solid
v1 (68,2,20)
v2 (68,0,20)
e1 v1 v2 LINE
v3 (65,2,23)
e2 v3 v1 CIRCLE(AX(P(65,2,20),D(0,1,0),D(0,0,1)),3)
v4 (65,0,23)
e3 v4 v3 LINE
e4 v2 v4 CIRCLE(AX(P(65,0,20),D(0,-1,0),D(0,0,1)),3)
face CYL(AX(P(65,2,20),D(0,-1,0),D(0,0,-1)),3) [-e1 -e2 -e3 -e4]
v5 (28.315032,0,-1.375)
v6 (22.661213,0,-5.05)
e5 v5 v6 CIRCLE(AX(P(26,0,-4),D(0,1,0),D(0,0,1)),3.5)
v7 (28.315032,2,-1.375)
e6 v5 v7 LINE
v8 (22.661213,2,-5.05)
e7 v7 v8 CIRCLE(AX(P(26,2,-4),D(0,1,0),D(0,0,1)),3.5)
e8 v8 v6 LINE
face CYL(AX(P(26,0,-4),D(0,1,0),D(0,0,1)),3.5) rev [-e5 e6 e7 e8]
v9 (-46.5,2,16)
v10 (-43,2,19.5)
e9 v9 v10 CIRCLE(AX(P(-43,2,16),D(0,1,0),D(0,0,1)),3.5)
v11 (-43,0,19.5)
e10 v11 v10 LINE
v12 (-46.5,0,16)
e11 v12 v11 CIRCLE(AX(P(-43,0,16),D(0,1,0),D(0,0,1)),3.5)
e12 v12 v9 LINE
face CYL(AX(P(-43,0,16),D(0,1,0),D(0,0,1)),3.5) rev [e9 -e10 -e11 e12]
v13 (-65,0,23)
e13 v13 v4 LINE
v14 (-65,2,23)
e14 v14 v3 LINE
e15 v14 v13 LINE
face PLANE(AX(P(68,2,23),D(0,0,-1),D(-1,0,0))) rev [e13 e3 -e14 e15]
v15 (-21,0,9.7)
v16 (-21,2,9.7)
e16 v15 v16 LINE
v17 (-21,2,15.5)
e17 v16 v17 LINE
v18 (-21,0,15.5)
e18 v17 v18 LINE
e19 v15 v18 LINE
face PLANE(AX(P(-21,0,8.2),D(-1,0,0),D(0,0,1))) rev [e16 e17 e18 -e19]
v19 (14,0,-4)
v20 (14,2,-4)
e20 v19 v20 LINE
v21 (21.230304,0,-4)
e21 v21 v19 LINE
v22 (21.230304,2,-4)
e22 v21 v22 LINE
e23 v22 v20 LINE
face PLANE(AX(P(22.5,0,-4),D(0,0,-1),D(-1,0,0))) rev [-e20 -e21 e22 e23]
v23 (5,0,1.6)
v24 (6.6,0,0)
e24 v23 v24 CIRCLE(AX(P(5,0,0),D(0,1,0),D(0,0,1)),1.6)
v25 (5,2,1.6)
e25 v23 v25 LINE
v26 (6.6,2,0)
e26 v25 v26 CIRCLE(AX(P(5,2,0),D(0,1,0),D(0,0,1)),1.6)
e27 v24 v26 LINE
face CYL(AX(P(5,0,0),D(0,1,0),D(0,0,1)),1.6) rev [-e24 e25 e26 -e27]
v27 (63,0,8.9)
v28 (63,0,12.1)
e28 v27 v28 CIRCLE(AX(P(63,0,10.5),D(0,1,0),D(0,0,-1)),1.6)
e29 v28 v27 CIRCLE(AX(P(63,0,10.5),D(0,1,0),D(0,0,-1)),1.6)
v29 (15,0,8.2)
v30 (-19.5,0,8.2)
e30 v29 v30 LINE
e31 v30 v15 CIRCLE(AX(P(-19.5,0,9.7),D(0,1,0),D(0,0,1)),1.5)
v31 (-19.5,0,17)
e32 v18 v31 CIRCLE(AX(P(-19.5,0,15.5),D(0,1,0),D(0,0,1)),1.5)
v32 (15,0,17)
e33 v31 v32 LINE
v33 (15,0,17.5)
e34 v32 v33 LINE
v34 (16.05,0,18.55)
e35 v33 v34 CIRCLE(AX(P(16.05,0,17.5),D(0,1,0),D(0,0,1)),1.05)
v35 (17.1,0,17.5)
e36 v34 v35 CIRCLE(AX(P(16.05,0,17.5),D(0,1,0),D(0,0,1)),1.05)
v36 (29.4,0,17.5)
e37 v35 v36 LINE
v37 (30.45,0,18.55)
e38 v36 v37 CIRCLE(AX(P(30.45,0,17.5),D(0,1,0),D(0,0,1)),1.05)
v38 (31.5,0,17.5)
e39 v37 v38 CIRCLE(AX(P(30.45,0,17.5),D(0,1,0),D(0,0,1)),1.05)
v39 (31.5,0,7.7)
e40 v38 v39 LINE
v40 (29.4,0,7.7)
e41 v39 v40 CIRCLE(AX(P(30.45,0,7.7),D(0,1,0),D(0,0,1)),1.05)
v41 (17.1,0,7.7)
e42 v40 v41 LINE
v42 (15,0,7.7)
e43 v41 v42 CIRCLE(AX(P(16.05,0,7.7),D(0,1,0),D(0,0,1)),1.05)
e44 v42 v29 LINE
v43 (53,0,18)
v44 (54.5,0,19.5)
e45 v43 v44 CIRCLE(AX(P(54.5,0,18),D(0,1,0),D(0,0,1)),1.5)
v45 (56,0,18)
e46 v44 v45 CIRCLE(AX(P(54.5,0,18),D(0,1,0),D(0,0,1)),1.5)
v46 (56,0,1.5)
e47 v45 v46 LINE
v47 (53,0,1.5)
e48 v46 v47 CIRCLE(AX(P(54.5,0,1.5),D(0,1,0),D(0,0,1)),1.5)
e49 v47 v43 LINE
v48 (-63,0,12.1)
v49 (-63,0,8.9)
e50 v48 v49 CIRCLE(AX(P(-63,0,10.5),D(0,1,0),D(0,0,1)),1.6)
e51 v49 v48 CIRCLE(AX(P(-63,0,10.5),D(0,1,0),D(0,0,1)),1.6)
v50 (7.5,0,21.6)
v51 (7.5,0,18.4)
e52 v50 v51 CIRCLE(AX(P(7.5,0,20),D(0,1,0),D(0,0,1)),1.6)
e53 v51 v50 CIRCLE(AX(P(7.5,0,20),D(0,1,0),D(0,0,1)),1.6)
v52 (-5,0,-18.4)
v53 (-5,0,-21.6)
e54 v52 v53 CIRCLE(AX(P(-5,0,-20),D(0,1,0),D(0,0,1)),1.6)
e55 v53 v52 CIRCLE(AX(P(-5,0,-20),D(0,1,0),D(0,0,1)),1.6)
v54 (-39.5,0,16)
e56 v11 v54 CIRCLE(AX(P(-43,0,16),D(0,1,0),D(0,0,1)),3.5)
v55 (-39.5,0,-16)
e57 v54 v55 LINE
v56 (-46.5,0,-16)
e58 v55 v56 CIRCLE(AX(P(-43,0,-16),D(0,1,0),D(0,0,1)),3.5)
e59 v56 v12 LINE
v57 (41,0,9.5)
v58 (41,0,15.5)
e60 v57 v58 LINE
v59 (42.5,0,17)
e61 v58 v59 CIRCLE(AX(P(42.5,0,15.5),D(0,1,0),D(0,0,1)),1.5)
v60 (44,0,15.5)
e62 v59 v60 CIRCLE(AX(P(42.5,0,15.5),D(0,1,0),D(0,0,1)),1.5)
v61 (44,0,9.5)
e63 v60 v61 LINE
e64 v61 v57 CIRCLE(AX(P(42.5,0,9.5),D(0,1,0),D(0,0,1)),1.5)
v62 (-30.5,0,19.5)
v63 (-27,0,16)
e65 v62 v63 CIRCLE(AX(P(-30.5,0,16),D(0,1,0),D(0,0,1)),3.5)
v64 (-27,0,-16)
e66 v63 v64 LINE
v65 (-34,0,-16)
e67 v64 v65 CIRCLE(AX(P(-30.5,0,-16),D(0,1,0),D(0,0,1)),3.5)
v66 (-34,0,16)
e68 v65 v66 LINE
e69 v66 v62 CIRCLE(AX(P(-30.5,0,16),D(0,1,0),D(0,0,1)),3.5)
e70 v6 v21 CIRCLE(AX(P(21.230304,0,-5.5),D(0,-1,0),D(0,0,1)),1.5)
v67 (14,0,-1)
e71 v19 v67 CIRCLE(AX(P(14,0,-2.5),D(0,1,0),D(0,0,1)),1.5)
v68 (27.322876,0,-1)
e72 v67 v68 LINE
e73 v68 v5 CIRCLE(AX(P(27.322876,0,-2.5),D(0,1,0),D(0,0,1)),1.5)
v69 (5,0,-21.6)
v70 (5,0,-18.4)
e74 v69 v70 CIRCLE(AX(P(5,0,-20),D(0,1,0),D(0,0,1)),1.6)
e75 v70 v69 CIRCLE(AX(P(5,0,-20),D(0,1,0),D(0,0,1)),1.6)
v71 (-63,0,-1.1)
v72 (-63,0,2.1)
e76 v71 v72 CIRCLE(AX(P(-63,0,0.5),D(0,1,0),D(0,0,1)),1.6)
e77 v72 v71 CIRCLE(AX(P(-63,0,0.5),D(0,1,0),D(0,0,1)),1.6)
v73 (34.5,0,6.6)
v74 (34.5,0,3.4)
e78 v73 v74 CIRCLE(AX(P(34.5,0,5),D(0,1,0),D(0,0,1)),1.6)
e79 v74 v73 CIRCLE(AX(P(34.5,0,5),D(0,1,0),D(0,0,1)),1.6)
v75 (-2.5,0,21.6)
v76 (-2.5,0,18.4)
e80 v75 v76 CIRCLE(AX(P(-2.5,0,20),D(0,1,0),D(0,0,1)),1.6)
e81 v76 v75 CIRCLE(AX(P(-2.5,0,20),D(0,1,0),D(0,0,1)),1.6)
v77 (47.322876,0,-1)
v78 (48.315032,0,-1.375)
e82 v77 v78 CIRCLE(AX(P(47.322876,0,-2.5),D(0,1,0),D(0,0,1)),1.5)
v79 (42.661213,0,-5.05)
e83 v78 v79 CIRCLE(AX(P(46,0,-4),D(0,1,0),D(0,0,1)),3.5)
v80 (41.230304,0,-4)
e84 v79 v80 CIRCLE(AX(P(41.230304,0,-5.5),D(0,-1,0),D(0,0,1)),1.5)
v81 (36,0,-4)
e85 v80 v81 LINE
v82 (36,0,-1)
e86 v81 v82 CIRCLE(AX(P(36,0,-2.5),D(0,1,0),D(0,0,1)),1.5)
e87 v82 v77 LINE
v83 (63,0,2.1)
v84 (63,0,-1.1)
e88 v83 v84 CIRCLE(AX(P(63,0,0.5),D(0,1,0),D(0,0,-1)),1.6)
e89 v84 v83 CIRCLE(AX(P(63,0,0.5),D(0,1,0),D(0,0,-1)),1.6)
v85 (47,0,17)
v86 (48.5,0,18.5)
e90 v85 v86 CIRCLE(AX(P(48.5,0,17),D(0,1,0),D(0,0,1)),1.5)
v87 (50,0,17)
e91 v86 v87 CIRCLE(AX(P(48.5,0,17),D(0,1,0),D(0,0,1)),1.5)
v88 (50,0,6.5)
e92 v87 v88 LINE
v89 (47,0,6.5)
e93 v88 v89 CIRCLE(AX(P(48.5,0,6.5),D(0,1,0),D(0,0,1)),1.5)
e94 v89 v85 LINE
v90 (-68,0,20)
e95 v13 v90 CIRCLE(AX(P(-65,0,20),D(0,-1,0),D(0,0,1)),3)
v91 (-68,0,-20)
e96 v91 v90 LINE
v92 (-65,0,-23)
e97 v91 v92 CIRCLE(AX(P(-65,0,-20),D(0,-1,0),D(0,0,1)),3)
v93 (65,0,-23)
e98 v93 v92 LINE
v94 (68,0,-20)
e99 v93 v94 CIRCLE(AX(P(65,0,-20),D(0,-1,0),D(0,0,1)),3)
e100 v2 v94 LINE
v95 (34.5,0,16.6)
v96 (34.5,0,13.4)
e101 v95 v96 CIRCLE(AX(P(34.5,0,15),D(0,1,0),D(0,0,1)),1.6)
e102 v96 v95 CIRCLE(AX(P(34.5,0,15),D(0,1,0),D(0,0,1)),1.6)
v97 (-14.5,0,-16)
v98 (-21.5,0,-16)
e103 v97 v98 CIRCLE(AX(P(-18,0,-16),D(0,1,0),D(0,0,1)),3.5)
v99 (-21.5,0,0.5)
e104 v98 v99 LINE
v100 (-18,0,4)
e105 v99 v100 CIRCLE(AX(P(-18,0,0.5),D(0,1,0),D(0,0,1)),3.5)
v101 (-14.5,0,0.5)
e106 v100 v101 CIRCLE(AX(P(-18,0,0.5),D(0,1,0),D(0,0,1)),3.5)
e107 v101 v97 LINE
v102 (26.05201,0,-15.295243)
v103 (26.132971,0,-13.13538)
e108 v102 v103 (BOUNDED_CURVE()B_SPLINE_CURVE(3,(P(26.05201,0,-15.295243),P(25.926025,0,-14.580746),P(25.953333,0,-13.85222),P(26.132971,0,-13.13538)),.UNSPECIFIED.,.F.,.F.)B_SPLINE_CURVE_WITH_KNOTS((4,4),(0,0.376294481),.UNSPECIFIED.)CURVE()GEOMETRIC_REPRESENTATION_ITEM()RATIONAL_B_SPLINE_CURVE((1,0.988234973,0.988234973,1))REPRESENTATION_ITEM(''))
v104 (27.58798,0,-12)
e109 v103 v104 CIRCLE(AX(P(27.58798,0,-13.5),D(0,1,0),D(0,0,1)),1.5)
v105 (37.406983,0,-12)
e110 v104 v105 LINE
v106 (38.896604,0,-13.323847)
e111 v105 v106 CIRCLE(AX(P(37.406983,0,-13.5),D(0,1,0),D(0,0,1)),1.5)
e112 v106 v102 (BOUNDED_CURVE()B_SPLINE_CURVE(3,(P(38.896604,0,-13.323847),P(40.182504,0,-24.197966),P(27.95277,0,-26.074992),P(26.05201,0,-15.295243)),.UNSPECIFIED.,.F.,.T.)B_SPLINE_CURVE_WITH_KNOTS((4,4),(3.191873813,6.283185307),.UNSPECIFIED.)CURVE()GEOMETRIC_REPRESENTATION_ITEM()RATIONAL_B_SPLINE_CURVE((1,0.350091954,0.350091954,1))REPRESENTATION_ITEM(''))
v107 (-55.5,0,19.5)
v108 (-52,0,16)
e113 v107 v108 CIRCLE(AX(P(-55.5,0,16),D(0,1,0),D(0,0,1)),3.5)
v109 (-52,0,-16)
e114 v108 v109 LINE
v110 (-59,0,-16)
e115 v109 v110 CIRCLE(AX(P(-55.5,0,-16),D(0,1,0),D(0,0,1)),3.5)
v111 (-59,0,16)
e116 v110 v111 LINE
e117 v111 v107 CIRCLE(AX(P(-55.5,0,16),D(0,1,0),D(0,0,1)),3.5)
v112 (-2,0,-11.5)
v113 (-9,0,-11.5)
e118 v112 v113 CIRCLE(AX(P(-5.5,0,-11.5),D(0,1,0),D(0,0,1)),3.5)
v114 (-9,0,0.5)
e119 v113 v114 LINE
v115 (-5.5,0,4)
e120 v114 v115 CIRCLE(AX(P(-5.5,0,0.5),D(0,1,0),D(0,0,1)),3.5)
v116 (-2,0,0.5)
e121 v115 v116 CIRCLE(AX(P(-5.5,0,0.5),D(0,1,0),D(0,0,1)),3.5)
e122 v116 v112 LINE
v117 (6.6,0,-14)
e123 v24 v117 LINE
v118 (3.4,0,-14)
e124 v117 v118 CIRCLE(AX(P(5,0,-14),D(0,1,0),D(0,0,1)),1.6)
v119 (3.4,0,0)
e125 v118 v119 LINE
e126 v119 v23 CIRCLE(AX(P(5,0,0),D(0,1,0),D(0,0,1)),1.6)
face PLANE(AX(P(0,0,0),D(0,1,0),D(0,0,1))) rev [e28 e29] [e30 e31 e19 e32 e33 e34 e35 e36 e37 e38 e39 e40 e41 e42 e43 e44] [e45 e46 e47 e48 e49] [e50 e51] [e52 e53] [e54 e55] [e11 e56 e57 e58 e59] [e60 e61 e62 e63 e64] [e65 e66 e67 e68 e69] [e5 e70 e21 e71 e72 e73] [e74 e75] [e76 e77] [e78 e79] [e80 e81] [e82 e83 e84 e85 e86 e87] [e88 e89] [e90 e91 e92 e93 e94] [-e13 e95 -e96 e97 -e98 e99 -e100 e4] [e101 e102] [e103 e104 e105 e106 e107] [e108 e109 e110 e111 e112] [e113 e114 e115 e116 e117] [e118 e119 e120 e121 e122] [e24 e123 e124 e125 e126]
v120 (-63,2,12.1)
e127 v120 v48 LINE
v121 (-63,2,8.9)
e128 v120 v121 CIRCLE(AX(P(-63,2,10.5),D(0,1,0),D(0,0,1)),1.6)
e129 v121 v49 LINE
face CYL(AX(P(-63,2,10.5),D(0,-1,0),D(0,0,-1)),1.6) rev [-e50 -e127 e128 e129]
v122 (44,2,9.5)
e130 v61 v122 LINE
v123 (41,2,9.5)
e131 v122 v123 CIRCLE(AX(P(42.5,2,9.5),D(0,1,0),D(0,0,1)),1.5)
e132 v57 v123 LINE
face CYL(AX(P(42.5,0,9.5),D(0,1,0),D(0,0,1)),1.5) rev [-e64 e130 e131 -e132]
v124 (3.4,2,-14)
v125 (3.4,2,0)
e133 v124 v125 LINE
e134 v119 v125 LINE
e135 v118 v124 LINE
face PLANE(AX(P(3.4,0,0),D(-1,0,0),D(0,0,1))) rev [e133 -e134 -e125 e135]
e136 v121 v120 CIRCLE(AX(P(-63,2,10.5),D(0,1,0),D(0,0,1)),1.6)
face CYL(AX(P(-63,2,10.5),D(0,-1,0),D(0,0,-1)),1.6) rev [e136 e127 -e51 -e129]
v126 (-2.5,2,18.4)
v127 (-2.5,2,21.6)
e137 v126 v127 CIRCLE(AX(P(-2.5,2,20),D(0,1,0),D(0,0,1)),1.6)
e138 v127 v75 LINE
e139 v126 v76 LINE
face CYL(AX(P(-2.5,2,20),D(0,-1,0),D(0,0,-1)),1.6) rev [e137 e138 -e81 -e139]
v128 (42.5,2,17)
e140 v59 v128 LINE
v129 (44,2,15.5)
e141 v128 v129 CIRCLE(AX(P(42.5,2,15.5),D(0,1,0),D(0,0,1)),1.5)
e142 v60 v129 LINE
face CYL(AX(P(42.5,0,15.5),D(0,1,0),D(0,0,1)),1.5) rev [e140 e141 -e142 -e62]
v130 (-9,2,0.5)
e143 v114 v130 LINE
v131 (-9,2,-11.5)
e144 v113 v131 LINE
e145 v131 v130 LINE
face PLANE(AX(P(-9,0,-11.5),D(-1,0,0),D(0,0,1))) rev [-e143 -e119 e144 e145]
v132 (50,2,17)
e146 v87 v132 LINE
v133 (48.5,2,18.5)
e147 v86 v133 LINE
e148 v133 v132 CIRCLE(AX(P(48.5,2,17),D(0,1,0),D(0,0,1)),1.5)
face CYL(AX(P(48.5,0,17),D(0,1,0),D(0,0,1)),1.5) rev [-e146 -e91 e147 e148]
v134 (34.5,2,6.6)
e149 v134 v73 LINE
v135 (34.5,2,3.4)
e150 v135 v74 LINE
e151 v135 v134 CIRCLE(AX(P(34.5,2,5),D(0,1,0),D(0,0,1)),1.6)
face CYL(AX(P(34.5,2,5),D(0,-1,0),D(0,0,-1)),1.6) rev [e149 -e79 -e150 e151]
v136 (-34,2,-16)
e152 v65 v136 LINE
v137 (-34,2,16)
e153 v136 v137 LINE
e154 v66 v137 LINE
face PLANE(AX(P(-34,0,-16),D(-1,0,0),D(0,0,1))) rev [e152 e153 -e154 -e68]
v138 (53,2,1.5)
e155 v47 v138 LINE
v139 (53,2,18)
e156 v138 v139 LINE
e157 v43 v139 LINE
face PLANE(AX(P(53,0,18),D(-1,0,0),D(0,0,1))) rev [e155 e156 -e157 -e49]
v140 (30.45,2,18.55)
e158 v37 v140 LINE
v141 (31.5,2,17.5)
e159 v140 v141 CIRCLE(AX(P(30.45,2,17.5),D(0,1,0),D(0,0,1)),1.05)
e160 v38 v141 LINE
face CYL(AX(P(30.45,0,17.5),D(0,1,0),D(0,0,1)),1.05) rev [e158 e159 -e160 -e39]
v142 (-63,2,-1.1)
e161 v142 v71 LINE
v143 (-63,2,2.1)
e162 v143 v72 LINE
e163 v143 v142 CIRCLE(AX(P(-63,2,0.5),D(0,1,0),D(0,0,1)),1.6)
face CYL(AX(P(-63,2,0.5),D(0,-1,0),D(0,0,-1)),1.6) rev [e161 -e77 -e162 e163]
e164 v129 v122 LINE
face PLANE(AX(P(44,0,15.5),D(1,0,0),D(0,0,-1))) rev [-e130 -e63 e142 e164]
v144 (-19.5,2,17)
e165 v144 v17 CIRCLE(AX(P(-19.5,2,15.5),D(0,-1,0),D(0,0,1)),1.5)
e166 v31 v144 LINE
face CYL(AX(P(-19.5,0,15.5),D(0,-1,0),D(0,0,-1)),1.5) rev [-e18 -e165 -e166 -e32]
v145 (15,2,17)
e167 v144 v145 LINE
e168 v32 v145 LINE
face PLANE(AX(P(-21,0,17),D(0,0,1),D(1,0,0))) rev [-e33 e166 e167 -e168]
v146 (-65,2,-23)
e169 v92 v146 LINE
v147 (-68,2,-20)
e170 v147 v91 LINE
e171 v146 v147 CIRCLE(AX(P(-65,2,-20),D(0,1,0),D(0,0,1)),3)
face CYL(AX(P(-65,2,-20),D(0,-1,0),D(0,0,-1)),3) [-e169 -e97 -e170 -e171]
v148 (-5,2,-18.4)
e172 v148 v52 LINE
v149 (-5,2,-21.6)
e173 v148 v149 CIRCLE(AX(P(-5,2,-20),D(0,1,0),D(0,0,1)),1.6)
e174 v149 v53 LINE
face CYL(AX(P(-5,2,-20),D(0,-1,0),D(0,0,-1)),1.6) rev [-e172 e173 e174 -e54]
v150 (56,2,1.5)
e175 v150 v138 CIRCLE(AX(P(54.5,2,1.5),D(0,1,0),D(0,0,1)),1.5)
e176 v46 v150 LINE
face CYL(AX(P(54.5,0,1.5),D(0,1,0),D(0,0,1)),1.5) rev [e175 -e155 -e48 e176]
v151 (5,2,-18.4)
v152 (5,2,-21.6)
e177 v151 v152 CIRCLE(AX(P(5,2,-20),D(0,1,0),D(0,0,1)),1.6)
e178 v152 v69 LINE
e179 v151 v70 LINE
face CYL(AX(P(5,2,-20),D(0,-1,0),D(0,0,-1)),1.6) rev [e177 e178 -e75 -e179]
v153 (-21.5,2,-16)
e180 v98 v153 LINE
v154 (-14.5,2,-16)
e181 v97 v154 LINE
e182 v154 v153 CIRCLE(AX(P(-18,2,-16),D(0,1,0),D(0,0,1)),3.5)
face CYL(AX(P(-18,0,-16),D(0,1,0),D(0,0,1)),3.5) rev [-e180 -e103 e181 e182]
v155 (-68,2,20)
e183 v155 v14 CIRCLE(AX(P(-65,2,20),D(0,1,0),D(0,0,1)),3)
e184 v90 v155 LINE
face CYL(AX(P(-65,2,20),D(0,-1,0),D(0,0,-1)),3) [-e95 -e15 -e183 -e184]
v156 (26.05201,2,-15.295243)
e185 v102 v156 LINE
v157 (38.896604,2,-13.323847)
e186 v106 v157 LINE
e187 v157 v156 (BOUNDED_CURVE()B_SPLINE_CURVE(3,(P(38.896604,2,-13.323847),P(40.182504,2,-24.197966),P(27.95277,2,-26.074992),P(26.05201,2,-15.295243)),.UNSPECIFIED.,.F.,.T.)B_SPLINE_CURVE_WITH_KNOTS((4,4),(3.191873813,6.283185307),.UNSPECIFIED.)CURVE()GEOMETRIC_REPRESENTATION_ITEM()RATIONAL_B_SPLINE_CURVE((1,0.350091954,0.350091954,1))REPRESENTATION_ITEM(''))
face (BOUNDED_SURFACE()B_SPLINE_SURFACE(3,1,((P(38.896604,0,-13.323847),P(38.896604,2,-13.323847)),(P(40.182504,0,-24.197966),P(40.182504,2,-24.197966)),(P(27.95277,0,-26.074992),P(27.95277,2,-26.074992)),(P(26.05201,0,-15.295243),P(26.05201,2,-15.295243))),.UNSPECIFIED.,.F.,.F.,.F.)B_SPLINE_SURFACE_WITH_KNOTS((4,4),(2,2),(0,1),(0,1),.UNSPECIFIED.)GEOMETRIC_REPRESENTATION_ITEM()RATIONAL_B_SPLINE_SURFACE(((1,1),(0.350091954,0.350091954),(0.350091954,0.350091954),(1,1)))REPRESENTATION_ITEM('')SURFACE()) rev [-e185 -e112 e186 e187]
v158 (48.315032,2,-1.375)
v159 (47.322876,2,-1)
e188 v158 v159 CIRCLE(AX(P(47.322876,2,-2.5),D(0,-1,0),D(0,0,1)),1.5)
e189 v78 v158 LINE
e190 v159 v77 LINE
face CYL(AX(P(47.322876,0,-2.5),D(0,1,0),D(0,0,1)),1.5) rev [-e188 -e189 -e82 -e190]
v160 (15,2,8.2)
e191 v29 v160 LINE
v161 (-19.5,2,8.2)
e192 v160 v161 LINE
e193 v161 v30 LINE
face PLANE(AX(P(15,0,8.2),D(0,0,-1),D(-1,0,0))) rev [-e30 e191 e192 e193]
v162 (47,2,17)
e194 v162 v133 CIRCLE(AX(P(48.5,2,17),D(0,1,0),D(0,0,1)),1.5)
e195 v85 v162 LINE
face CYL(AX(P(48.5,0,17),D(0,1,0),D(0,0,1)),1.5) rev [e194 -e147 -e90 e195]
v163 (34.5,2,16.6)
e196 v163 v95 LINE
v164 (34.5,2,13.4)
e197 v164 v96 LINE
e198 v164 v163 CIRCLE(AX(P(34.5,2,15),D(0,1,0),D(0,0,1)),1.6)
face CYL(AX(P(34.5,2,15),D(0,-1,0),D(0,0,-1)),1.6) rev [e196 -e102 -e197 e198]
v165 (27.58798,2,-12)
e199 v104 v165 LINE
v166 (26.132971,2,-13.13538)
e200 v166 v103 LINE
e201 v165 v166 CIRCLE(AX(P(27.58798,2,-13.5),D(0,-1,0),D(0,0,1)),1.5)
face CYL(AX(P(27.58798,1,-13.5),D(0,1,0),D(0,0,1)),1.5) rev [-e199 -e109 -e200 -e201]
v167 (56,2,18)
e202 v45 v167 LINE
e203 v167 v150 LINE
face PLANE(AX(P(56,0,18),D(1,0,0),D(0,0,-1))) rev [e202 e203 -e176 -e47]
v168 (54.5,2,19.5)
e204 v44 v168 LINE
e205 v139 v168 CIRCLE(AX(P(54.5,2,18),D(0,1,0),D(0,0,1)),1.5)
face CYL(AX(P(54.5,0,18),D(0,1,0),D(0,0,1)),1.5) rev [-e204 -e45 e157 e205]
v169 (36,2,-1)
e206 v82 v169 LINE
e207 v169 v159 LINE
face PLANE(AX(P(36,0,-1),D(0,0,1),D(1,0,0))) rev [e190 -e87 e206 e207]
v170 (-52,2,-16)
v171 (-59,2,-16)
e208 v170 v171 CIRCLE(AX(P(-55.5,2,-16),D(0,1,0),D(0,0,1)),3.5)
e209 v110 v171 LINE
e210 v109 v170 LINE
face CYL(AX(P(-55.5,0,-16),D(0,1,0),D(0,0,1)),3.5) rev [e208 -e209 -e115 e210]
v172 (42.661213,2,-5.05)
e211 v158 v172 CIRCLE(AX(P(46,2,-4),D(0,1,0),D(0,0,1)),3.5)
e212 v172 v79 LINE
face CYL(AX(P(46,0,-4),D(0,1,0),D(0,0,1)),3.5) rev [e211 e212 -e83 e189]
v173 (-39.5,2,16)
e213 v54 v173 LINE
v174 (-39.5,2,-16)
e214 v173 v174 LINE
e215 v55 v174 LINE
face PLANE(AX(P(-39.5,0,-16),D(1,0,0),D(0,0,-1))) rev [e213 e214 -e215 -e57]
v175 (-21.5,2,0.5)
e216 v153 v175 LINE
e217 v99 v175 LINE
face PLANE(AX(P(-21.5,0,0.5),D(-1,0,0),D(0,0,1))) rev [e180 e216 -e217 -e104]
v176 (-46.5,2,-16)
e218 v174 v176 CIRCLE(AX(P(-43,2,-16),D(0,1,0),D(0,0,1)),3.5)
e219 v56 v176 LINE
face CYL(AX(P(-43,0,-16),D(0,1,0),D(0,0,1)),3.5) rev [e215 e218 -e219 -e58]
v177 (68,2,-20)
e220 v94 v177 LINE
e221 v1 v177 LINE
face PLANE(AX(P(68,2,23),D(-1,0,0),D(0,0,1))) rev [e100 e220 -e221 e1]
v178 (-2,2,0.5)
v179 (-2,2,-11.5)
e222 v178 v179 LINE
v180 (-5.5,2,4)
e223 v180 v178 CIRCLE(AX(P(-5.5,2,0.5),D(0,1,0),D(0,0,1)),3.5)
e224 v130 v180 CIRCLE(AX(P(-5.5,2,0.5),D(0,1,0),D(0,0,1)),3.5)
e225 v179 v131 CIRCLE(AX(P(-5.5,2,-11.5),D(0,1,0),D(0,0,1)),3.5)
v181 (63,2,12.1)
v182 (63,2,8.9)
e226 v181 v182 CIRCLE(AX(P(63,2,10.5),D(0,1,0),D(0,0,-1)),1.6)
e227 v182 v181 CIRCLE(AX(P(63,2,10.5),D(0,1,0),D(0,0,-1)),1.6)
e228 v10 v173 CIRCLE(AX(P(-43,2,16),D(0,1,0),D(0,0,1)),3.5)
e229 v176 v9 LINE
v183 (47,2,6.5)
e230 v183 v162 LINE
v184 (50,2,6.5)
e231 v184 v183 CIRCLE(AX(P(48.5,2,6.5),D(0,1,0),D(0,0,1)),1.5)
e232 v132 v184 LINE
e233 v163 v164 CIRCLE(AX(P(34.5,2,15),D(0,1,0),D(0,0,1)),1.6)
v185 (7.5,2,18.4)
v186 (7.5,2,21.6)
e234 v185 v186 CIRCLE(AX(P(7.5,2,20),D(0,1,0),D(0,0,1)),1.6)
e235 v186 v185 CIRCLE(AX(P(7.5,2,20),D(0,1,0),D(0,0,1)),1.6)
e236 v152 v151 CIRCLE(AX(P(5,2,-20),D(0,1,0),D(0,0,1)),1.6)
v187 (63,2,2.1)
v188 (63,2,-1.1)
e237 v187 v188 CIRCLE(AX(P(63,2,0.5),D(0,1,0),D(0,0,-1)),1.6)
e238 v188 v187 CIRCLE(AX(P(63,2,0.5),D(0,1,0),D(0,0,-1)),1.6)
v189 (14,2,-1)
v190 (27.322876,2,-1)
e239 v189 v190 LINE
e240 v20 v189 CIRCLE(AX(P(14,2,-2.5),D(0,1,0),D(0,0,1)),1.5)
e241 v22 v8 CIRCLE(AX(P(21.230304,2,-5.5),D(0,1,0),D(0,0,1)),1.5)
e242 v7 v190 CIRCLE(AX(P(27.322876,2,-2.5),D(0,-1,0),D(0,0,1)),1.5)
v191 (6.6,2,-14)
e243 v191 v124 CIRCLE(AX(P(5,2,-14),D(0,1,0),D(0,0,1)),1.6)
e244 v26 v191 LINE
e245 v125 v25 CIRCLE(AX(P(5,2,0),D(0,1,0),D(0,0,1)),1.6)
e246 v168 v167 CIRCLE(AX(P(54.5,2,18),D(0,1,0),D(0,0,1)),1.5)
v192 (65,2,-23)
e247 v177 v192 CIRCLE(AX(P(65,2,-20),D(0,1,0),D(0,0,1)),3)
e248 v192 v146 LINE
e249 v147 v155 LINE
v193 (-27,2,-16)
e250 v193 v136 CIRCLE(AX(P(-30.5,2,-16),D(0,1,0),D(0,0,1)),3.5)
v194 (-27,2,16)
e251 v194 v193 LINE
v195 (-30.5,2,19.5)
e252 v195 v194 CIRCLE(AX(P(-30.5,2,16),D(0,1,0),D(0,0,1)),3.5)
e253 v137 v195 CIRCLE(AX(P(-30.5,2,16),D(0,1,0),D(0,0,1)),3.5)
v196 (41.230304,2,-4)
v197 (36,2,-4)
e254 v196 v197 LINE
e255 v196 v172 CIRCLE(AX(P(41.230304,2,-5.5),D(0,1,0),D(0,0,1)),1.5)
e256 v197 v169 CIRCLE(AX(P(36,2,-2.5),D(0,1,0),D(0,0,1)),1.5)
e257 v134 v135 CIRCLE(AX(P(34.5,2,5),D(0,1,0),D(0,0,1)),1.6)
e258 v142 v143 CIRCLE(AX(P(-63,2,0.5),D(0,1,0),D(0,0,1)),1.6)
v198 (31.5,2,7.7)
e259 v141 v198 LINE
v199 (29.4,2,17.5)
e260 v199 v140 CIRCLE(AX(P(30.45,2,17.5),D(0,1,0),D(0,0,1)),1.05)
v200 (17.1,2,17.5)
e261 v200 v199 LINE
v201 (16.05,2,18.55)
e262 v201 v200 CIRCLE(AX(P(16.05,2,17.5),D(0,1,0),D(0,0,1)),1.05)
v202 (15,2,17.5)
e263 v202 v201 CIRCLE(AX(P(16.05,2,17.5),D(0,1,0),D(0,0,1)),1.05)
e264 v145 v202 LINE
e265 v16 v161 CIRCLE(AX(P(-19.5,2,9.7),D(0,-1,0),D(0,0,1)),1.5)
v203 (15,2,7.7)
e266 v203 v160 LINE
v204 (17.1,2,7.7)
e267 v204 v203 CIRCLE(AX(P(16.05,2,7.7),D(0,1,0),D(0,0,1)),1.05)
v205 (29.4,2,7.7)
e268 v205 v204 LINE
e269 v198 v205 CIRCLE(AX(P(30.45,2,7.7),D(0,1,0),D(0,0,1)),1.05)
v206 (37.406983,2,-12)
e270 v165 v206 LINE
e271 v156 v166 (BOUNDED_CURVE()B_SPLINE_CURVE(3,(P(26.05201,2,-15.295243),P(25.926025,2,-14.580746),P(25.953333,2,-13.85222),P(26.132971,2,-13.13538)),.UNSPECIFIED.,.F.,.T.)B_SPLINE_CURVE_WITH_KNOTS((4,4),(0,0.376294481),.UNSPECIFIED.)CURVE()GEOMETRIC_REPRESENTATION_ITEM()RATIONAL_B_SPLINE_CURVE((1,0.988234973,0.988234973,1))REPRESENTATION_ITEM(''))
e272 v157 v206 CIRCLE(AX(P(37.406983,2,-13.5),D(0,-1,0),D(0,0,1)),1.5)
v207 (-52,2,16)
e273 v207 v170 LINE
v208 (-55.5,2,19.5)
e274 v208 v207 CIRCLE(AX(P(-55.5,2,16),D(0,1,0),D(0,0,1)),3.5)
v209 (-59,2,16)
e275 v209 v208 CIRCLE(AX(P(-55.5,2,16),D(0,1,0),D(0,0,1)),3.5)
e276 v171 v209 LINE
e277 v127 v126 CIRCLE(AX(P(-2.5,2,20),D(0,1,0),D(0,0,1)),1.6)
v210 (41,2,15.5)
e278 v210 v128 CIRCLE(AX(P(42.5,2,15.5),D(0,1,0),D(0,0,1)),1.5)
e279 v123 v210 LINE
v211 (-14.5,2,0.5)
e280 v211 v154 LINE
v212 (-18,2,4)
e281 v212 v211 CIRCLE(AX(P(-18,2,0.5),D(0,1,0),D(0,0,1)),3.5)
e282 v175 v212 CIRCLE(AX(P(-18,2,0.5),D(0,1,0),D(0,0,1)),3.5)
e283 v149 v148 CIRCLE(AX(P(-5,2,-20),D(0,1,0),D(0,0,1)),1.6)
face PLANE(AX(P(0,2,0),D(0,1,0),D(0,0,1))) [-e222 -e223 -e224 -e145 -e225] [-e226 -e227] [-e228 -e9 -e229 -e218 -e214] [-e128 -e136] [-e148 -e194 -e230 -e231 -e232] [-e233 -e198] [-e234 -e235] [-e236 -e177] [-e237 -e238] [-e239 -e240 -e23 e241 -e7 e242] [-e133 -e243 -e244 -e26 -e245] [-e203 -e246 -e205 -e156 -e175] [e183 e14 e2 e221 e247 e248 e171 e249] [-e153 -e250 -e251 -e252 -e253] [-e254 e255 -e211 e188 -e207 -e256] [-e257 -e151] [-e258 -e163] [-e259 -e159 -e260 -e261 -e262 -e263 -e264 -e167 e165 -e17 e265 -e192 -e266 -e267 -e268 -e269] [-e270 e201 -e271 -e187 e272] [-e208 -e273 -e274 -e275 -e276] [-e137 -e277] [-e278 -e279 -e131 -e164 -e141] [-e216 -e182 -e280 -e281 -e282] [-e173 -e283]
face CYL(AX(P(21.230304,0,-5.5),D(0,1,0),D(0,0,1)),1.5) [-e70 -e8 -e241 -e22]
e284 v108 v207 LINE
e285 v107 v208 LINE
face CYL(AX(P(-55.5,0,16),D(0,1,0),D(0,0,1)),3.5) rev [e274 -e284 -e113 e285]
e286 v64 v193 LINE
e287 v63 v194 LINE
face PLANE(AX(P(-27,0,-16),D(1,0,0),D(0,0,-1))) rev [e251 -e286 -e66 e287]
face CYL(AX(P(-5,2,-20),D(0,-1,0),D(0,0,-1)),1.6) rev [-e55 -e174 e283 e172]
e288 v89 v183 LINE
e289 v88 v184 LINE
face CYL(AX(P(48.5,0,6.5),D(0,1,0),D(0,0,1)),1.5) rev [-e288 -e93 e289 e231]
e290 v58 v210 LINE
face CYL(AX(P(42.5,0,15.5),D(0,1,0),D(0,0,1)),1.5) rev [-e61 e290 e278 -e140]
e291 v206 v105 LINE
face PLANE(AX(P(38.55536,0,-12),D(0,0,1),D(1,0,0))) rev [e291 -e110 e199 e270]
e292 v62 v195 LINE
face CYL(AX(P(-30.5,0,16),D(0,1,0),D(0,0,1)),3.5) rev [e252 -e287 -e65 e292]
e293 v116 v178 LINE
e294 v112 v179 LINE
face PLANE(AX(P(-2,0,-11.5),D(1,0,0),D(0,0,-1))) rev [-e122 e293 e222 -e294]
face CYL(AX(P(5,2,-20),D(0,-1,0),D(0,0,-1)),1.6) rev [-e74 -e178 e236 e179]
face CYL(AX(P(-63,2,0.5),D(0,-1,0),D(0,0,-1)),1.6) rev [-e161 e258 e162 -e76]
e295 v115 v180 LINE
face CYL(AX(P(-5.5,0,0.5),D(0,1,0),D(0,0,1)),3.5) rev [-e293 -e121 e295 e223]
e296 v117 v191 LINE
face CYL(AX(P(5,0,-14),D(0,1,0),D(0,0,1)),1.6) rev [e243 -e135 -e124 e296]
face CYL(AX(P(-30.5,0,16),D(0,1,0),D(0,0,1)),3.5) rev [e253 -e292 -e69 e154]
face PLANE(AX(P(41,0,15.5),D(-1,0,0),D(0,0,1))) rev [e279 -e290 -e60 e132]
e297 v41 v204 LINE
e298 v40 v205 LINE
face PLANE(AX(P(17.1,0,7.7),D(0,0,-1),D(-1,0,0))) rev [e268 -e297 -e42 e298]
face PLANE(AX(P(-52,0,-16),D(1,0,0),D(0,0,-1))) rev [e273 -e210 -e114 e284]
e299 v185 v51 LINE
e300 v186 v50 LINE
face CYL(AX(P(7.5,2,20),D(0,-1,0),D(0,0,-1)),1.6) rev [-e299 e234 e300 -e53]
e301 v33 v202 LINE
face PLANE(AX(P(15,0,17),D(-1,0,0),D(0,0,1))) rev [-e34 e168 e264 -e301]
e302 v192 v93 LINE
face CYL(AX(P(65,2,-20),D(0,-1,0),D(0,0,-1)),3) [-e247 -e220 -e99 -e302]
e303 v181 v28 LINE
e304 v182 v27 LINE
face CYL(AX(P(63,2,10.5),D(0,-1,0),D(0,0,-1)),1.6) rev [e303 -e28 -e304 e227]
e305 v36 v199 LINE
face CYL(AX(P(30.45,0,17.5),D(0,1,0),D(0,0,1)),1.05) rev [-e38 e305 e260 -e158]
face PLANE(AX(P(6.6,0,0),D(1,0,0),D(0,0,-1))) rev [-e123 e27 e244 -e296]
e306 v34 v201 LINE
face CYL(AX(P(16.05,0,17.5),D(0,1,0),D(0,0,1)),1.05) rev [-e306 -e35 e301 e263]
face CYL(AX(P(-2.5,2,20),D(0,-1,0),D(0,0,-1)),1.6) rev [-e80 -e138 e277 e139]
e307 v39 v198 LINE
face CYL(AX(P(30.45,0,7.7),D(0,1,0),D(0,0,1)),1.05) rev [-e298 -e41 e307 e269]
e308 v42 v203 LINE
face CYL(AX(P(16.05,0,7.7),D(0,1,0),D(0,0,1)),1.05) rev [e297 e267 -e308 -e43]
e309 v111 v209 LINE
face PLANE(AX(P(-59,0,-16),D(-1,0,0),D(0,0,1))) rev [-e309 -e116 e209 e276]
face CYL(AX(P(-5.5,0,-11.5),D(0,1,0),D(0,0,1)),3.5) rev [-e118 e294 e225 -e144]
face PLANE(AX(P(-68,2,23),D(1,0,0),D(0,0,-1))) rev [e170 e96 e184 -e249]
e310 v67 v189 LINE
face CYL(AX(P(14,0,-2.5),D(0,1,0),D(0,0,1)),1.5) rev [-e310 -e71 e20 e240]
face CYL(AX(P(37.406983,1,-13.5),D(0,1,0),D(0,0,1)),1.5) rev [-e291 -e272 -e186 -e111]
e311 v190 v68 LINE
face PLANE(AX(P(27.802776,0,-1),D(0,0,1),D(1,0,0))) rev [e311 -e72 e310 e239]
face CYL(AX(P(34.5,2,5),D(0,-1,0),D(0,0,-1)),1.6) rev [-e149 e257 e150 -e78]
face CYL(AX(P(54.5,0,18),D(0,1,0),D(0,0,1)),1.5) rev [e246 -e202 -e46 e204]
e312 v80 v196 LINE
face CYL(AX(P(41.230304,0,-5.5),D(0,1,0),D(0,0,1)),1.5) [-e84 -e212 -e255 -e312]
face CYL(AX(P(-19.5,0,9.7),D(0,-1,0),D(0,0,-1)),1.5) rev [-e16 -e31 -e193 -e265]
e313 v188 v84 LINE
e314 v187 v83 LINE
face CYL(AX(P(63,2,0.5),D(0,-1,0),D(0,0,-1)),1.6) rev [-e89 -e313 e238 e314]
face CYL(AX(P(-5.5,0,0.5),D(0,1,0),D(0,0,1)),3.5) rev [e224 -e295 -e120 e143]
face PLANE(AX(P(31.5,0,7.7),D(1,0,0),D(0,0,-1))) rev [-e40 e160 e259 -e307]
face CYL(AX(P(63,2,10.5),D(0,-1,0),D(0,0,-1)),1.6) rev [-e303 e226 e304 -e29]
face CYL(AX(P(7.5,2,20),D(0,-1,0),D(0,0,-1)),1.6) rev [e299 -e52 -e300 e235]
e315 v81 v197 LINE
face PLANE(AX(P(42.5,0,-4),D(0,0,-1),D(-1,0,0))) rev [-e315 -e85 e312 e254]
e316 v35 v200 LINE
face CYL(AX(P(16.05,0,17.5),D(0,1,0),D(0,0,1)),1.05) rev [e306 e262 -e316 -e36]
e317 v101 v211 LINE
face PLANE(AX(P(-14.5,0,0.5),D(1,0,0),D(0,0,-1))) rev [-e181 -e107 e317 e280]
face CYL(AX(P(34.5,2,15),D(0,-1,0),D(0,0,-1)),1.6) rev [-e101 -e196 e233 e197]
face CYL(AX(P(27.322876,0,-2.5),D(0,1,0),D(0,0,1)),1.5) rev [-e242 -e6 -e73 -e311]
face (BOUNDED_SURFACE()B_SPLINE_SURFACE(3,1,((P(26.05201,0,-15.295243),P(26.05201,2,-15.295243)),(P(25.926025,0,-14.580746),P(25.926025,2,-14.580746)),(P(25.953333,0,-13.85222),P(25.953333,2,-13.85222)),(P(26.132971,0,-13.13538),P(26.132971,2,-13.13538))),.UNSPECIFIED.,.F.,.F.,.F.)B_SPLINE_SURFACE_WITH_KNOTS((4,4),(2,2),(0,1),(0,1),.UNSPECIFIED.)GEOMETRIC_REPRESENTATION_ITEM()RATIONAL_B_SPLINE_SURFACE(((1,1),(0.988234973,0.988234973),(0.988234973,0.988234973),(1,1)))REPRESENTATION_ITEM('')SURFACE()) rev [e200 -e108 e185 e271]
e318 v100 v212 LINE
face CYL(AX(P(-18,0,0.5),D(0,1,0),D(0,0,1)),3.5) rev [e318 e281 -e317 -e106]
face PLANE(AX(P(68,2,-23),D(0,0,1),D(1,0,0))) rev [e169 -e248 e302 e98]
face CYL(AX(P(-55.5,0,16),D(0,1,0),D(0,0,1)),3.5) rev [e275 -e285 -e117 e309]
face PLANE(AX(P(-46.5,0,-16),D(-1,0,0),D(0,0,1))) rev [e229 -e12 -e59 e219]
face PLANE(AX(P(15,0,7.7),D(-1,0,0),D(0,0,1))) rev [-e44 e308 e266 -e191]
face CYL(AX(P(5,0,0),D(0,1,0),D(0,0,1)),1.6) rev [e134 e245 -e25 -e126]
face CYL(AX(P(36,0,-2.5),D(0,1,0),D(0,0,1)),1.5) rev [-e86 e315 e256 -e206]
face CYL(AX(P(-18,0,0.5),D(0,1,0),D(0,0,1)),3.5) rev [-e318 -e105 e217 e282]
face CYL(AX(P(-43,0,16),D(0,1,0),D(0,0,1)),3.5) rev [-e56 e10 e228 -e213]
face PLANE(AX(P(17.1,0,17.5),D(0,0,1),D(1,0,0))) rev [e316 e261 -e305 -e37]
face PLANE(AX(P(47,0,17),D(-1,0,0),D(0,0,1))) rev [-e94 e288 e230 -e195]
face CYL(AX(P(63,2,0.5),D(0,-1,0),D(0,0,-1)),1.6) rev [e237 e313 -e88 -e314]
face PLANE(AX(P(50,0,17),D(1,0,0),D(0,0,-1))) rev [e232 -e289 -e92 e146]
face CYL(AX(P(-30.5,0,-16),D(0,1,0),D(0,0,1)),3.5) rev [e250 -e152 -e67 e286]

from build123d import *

# Parameters (mm, degrees)
SKETCH1_W              = 136
SKETCH1_H              = 46
SKETCH1_R              = 1.6
BOSS_EXTRUDE1_DEPTH    = 2
CUT_EXTRUDE1_DEPTH     = 72.812255222
R1_5_CUTOUT_FILLET_R   = 1.5
R3_OUTER_EDGE_FILLET_R = 3


with BuildPart() as part:
    # Sketch1 → Boss-Extrude1 (new body)
    with BuildSketch(Plane(origin=(0, 0, 0), x_dir=(1, 0, 0), z_dir=(0, 1, 0))):
        Rectangle(SKETCH1_W, SKETCH1_H)
        with Locations(Location((-63, -0.5, 0), (0, 0, 270))):
            Circle(SKETCH1_R, mode=Mode.SUBTRACT)
        with Locations(Location((-63, -10.5, 0), (0, 0, 270))):
            Circle(SKETCH1_R, mode=Mode.SUBTRACT)
        with Locations(Location((-2.5, -20, 0), (0, 0, 270))):
            Circle(SKETCH1_R, mode=Mode.SUBTRACT)
        with Locations(Location((7.5, -20, 0), (0, 0, 270))):
            Circle(SKETCH1_R, mode=Mode.SUBTRACT)
        with Locations(Location((63, -10.5, 0), (0, 0, 90))):
            Circle(SKETCH1_R, mode=Mode.SUBTRACT)
        with Locations(Location((63, -0.5, 0), (0, 0, 90))):
            Circle(SKETCH1_R, mode=Mode.SUBTRACT)
        with Locations(Location((5, 20, 0), (0, 0, 270))):
            Circle(SKETCH1_R, mode=Mode.SUBTRACT)
        with Locations(Location((-5, 20, 0), (0, 0, 270))):
            Circle(SKETCH1_R, mode=Mode.SUBTRACT)
        with Locations(Location((34.5, -5, 0), (0, 0, 270))):
            Circle(SKETCH1_R, mode=Mode.SUBTRACT)
        with Locations(Location((34.5, -15, 0), (0, 0, 270))):
            Circle(SKETCH1_R, mode=Mode.SUBTRACT)
    extrude(amount=BOSS_EXTRUDE1_DEPTH)

    # Sketch2 → Cut-Extrude1 (cut, through all)
    with BuildSketch(Plane(origin=(0, 2, 0), x_dir=(1, 0, 0), z_dir=(0, 1, 0))):
        with BuildLine():
            Line((-52, 16), (-52, -16))
            ThreePointArc((-52, -16), (-55.5, -19.5), (-59, -16))
            Line((-59, -16), (-59, 16))
            ThreePointArc((-59, 16), (-55.5, 19.5), (-52, 16))
        make_face()
        with BuildLine():
            Line((17.1, -7.7), (29.4, -7.7))
            ThreePointArc((29.4, -7.7), (30.45, -6.65), (31.5, -7.7))
            Line((31.5, -7.7), (31.5, -17.5))
            ThreePointArc((31.5, -17.5), (30.45, -18.55), (29.4, -17.5))
            Line((29.4, -17.5), (17.1, -17.5))
            ThreePointArc((17.1, -17.5), (16.05, -18.55), (15, -17.5))
            Line((15, -17.5), (15, -17))
            Line((15, -17), (-21, -17))
            Line((-21, -17), (-21, -8.2))
            Line((-21, -8.2), (15, -8.2))
            Line((15, -8.2), (15, -7.7))
            ThreePointArc((15, -7.7), (16.05, -6.65), (17.1, -7.7))
        make_face()
        with BuildLine():
            Line((-39.5, 16), (-39.5, -16))
            ThreePointArc((-39.5, -16), (-43, -19.5), (-46.5, -16))
            Line((-46.5, -16), (-46.5, 16))
            ThreePointArc((-46.5, 16), (-43, 19.5), (-39.5, 16))
        make_face()
        with BuildLine():
            Line((-27, 16), (-27, -16))
            ThreePointArc((-27, -16), (-30.5, -19.5), (-34, -16))
            Line((-34, -16), (-34, 16))
            ThreePointArc((-34, 16), (-30.5, 19.5), (-27, 16))
        make_face()
        with BuildLine():
            Line((-2, 11.5), (-2, -0.5))
            ThreePointArc((-2, -0.5), (-5.5, -4), (-9, -0.5))
            Line((-9, -0.5), (-9, 11.5))
            ThreePointArc((-9, 11.5), (-5.5, 15), (-2, 11.5))
        make_face()
        with BuildLine():
            Line((42.5, 4), (36, 4))
            ThreePointArc((36, 4), (34.5, 2.5), (36, 1))
            Line((36, 1), (47.802775638, 1))
            ThreePointArc((47.802775638, 1), (47.723410176, 7.046285831), (42.5, 4))
        make_face()
        with BuildLine():
            Line((41, -15.5), (41, -9.5))
            ThreePointArc((41, -9.5), (42.5, -8), (44, -9.5))
            Line((44, -9.5), (44, -15.5))
            ThreePointArc((44, -15.5), (42.5, -17), (41, -15.5))
        make_face()
        with BuildLine():
            Line((47, -17), (47, -6.5))
            ThreePointArc((47, -6.5), (48.5, -5), (50, -6.5))
            Line((50, -6.5), (50, -17))
            ThreePointArc((50, -17), (48.5, -18.5), (47, -17))
        make_face()
        with BuildLine():
            Line((53, -18), (53, -1.5))
            ThreePointArc((53, -1.5), (54.5, 0), (56, -1.5))
            Line((56, -1.5), (56, -18))
            ThreePointArc((56, -18), (54.5, -19.5), (53, -18))
        make_face()
        with BuildLine():
            Line((22.5, 4), (14, 4))
            ThreePointArc((14, 4), (12.5, 2.5), (14, 1))
            Line((14, 1), (27.802775638, 1))
            ThreePointArc((27.802775638, 1), (27.723410176, 7.046285831), (22.5, 4))
        make_face()
        with BuildLine():
            Line((38.555359619, 12), (26.555359619, 12))
            add(Edge.make_bspline(
                [(38.555359619, 12), (41.784518916, 19.940569638), (32.181153285, 19.940569638), (22.577787653, 19.940569638), (26.555359619, 12)],
                knots=[6.095299784, 6.095299784, 6.095299784, 8.050729179, 8.050729179, 10.006158574, 10.006158574, 10.006158574], degree=2, weights=[1, 0.558919028, 1, 0.558919028, 1]))
        make_face()
        with BuildLine():
            Line((3.4, 0), (3.4, 14))
            ThreePointArc((3.4, 14), (5, 15.6), (6.6, 14))
            Line((6.6, 14), (6.6, 0))
            ThreePointArc((6.6, 0), (5, -1.6), (3.4, 0))
        make_face()
        with BuildLine():
            Line((-21.5, -0.5), (-21.5, 16))
            ThreePointArc((-21.5, 16), (-18, 19.5), (-14.5, 16))
            Line((-14.5, 16), (-14.5, -0.5))
            ThreePointArc((-14.5, -0.5), (-18, -4), (-21.5, -0.5))
        make_face()
    extrude(amount=-CUT_EXTRUDE1_DEPTH, mode=Mode.SUBTRACT)

    # R1.5 cutout fillet
    r1_5_cutout_fillet_edges = [part.edges().sort_by_distance(p)[0] for p in [
        (-21, 1, 8.2),
        (-21, 1, 17),
        (38.555359619, 1, -12),
        (26.555359619, 1, -12),
        (22.5, 1, -4),
        (27.802775638, 1, -1),
        (42.5, 1, -4),
        (47.802775638, 1, -1),
    ]]
    fillet(r1_5_cutout_fillet_edges, radius=R1_5_CUTOUT_FILLET_R)

    # R3 outer edge fillet
    r3_outer_edge_fillet_edges = [part.edges().sort_by_distance(p)[0] for p in [
        (-68, 1, -23),
        (68, 1, -23),
        (68, 1, 23),
        (-68, 1, 23),
    ]]
    fillet(r3_outer_edge_fillet_edges, radius=R3_OUTER_EDGE_FILLET_R)


solid = part.part
